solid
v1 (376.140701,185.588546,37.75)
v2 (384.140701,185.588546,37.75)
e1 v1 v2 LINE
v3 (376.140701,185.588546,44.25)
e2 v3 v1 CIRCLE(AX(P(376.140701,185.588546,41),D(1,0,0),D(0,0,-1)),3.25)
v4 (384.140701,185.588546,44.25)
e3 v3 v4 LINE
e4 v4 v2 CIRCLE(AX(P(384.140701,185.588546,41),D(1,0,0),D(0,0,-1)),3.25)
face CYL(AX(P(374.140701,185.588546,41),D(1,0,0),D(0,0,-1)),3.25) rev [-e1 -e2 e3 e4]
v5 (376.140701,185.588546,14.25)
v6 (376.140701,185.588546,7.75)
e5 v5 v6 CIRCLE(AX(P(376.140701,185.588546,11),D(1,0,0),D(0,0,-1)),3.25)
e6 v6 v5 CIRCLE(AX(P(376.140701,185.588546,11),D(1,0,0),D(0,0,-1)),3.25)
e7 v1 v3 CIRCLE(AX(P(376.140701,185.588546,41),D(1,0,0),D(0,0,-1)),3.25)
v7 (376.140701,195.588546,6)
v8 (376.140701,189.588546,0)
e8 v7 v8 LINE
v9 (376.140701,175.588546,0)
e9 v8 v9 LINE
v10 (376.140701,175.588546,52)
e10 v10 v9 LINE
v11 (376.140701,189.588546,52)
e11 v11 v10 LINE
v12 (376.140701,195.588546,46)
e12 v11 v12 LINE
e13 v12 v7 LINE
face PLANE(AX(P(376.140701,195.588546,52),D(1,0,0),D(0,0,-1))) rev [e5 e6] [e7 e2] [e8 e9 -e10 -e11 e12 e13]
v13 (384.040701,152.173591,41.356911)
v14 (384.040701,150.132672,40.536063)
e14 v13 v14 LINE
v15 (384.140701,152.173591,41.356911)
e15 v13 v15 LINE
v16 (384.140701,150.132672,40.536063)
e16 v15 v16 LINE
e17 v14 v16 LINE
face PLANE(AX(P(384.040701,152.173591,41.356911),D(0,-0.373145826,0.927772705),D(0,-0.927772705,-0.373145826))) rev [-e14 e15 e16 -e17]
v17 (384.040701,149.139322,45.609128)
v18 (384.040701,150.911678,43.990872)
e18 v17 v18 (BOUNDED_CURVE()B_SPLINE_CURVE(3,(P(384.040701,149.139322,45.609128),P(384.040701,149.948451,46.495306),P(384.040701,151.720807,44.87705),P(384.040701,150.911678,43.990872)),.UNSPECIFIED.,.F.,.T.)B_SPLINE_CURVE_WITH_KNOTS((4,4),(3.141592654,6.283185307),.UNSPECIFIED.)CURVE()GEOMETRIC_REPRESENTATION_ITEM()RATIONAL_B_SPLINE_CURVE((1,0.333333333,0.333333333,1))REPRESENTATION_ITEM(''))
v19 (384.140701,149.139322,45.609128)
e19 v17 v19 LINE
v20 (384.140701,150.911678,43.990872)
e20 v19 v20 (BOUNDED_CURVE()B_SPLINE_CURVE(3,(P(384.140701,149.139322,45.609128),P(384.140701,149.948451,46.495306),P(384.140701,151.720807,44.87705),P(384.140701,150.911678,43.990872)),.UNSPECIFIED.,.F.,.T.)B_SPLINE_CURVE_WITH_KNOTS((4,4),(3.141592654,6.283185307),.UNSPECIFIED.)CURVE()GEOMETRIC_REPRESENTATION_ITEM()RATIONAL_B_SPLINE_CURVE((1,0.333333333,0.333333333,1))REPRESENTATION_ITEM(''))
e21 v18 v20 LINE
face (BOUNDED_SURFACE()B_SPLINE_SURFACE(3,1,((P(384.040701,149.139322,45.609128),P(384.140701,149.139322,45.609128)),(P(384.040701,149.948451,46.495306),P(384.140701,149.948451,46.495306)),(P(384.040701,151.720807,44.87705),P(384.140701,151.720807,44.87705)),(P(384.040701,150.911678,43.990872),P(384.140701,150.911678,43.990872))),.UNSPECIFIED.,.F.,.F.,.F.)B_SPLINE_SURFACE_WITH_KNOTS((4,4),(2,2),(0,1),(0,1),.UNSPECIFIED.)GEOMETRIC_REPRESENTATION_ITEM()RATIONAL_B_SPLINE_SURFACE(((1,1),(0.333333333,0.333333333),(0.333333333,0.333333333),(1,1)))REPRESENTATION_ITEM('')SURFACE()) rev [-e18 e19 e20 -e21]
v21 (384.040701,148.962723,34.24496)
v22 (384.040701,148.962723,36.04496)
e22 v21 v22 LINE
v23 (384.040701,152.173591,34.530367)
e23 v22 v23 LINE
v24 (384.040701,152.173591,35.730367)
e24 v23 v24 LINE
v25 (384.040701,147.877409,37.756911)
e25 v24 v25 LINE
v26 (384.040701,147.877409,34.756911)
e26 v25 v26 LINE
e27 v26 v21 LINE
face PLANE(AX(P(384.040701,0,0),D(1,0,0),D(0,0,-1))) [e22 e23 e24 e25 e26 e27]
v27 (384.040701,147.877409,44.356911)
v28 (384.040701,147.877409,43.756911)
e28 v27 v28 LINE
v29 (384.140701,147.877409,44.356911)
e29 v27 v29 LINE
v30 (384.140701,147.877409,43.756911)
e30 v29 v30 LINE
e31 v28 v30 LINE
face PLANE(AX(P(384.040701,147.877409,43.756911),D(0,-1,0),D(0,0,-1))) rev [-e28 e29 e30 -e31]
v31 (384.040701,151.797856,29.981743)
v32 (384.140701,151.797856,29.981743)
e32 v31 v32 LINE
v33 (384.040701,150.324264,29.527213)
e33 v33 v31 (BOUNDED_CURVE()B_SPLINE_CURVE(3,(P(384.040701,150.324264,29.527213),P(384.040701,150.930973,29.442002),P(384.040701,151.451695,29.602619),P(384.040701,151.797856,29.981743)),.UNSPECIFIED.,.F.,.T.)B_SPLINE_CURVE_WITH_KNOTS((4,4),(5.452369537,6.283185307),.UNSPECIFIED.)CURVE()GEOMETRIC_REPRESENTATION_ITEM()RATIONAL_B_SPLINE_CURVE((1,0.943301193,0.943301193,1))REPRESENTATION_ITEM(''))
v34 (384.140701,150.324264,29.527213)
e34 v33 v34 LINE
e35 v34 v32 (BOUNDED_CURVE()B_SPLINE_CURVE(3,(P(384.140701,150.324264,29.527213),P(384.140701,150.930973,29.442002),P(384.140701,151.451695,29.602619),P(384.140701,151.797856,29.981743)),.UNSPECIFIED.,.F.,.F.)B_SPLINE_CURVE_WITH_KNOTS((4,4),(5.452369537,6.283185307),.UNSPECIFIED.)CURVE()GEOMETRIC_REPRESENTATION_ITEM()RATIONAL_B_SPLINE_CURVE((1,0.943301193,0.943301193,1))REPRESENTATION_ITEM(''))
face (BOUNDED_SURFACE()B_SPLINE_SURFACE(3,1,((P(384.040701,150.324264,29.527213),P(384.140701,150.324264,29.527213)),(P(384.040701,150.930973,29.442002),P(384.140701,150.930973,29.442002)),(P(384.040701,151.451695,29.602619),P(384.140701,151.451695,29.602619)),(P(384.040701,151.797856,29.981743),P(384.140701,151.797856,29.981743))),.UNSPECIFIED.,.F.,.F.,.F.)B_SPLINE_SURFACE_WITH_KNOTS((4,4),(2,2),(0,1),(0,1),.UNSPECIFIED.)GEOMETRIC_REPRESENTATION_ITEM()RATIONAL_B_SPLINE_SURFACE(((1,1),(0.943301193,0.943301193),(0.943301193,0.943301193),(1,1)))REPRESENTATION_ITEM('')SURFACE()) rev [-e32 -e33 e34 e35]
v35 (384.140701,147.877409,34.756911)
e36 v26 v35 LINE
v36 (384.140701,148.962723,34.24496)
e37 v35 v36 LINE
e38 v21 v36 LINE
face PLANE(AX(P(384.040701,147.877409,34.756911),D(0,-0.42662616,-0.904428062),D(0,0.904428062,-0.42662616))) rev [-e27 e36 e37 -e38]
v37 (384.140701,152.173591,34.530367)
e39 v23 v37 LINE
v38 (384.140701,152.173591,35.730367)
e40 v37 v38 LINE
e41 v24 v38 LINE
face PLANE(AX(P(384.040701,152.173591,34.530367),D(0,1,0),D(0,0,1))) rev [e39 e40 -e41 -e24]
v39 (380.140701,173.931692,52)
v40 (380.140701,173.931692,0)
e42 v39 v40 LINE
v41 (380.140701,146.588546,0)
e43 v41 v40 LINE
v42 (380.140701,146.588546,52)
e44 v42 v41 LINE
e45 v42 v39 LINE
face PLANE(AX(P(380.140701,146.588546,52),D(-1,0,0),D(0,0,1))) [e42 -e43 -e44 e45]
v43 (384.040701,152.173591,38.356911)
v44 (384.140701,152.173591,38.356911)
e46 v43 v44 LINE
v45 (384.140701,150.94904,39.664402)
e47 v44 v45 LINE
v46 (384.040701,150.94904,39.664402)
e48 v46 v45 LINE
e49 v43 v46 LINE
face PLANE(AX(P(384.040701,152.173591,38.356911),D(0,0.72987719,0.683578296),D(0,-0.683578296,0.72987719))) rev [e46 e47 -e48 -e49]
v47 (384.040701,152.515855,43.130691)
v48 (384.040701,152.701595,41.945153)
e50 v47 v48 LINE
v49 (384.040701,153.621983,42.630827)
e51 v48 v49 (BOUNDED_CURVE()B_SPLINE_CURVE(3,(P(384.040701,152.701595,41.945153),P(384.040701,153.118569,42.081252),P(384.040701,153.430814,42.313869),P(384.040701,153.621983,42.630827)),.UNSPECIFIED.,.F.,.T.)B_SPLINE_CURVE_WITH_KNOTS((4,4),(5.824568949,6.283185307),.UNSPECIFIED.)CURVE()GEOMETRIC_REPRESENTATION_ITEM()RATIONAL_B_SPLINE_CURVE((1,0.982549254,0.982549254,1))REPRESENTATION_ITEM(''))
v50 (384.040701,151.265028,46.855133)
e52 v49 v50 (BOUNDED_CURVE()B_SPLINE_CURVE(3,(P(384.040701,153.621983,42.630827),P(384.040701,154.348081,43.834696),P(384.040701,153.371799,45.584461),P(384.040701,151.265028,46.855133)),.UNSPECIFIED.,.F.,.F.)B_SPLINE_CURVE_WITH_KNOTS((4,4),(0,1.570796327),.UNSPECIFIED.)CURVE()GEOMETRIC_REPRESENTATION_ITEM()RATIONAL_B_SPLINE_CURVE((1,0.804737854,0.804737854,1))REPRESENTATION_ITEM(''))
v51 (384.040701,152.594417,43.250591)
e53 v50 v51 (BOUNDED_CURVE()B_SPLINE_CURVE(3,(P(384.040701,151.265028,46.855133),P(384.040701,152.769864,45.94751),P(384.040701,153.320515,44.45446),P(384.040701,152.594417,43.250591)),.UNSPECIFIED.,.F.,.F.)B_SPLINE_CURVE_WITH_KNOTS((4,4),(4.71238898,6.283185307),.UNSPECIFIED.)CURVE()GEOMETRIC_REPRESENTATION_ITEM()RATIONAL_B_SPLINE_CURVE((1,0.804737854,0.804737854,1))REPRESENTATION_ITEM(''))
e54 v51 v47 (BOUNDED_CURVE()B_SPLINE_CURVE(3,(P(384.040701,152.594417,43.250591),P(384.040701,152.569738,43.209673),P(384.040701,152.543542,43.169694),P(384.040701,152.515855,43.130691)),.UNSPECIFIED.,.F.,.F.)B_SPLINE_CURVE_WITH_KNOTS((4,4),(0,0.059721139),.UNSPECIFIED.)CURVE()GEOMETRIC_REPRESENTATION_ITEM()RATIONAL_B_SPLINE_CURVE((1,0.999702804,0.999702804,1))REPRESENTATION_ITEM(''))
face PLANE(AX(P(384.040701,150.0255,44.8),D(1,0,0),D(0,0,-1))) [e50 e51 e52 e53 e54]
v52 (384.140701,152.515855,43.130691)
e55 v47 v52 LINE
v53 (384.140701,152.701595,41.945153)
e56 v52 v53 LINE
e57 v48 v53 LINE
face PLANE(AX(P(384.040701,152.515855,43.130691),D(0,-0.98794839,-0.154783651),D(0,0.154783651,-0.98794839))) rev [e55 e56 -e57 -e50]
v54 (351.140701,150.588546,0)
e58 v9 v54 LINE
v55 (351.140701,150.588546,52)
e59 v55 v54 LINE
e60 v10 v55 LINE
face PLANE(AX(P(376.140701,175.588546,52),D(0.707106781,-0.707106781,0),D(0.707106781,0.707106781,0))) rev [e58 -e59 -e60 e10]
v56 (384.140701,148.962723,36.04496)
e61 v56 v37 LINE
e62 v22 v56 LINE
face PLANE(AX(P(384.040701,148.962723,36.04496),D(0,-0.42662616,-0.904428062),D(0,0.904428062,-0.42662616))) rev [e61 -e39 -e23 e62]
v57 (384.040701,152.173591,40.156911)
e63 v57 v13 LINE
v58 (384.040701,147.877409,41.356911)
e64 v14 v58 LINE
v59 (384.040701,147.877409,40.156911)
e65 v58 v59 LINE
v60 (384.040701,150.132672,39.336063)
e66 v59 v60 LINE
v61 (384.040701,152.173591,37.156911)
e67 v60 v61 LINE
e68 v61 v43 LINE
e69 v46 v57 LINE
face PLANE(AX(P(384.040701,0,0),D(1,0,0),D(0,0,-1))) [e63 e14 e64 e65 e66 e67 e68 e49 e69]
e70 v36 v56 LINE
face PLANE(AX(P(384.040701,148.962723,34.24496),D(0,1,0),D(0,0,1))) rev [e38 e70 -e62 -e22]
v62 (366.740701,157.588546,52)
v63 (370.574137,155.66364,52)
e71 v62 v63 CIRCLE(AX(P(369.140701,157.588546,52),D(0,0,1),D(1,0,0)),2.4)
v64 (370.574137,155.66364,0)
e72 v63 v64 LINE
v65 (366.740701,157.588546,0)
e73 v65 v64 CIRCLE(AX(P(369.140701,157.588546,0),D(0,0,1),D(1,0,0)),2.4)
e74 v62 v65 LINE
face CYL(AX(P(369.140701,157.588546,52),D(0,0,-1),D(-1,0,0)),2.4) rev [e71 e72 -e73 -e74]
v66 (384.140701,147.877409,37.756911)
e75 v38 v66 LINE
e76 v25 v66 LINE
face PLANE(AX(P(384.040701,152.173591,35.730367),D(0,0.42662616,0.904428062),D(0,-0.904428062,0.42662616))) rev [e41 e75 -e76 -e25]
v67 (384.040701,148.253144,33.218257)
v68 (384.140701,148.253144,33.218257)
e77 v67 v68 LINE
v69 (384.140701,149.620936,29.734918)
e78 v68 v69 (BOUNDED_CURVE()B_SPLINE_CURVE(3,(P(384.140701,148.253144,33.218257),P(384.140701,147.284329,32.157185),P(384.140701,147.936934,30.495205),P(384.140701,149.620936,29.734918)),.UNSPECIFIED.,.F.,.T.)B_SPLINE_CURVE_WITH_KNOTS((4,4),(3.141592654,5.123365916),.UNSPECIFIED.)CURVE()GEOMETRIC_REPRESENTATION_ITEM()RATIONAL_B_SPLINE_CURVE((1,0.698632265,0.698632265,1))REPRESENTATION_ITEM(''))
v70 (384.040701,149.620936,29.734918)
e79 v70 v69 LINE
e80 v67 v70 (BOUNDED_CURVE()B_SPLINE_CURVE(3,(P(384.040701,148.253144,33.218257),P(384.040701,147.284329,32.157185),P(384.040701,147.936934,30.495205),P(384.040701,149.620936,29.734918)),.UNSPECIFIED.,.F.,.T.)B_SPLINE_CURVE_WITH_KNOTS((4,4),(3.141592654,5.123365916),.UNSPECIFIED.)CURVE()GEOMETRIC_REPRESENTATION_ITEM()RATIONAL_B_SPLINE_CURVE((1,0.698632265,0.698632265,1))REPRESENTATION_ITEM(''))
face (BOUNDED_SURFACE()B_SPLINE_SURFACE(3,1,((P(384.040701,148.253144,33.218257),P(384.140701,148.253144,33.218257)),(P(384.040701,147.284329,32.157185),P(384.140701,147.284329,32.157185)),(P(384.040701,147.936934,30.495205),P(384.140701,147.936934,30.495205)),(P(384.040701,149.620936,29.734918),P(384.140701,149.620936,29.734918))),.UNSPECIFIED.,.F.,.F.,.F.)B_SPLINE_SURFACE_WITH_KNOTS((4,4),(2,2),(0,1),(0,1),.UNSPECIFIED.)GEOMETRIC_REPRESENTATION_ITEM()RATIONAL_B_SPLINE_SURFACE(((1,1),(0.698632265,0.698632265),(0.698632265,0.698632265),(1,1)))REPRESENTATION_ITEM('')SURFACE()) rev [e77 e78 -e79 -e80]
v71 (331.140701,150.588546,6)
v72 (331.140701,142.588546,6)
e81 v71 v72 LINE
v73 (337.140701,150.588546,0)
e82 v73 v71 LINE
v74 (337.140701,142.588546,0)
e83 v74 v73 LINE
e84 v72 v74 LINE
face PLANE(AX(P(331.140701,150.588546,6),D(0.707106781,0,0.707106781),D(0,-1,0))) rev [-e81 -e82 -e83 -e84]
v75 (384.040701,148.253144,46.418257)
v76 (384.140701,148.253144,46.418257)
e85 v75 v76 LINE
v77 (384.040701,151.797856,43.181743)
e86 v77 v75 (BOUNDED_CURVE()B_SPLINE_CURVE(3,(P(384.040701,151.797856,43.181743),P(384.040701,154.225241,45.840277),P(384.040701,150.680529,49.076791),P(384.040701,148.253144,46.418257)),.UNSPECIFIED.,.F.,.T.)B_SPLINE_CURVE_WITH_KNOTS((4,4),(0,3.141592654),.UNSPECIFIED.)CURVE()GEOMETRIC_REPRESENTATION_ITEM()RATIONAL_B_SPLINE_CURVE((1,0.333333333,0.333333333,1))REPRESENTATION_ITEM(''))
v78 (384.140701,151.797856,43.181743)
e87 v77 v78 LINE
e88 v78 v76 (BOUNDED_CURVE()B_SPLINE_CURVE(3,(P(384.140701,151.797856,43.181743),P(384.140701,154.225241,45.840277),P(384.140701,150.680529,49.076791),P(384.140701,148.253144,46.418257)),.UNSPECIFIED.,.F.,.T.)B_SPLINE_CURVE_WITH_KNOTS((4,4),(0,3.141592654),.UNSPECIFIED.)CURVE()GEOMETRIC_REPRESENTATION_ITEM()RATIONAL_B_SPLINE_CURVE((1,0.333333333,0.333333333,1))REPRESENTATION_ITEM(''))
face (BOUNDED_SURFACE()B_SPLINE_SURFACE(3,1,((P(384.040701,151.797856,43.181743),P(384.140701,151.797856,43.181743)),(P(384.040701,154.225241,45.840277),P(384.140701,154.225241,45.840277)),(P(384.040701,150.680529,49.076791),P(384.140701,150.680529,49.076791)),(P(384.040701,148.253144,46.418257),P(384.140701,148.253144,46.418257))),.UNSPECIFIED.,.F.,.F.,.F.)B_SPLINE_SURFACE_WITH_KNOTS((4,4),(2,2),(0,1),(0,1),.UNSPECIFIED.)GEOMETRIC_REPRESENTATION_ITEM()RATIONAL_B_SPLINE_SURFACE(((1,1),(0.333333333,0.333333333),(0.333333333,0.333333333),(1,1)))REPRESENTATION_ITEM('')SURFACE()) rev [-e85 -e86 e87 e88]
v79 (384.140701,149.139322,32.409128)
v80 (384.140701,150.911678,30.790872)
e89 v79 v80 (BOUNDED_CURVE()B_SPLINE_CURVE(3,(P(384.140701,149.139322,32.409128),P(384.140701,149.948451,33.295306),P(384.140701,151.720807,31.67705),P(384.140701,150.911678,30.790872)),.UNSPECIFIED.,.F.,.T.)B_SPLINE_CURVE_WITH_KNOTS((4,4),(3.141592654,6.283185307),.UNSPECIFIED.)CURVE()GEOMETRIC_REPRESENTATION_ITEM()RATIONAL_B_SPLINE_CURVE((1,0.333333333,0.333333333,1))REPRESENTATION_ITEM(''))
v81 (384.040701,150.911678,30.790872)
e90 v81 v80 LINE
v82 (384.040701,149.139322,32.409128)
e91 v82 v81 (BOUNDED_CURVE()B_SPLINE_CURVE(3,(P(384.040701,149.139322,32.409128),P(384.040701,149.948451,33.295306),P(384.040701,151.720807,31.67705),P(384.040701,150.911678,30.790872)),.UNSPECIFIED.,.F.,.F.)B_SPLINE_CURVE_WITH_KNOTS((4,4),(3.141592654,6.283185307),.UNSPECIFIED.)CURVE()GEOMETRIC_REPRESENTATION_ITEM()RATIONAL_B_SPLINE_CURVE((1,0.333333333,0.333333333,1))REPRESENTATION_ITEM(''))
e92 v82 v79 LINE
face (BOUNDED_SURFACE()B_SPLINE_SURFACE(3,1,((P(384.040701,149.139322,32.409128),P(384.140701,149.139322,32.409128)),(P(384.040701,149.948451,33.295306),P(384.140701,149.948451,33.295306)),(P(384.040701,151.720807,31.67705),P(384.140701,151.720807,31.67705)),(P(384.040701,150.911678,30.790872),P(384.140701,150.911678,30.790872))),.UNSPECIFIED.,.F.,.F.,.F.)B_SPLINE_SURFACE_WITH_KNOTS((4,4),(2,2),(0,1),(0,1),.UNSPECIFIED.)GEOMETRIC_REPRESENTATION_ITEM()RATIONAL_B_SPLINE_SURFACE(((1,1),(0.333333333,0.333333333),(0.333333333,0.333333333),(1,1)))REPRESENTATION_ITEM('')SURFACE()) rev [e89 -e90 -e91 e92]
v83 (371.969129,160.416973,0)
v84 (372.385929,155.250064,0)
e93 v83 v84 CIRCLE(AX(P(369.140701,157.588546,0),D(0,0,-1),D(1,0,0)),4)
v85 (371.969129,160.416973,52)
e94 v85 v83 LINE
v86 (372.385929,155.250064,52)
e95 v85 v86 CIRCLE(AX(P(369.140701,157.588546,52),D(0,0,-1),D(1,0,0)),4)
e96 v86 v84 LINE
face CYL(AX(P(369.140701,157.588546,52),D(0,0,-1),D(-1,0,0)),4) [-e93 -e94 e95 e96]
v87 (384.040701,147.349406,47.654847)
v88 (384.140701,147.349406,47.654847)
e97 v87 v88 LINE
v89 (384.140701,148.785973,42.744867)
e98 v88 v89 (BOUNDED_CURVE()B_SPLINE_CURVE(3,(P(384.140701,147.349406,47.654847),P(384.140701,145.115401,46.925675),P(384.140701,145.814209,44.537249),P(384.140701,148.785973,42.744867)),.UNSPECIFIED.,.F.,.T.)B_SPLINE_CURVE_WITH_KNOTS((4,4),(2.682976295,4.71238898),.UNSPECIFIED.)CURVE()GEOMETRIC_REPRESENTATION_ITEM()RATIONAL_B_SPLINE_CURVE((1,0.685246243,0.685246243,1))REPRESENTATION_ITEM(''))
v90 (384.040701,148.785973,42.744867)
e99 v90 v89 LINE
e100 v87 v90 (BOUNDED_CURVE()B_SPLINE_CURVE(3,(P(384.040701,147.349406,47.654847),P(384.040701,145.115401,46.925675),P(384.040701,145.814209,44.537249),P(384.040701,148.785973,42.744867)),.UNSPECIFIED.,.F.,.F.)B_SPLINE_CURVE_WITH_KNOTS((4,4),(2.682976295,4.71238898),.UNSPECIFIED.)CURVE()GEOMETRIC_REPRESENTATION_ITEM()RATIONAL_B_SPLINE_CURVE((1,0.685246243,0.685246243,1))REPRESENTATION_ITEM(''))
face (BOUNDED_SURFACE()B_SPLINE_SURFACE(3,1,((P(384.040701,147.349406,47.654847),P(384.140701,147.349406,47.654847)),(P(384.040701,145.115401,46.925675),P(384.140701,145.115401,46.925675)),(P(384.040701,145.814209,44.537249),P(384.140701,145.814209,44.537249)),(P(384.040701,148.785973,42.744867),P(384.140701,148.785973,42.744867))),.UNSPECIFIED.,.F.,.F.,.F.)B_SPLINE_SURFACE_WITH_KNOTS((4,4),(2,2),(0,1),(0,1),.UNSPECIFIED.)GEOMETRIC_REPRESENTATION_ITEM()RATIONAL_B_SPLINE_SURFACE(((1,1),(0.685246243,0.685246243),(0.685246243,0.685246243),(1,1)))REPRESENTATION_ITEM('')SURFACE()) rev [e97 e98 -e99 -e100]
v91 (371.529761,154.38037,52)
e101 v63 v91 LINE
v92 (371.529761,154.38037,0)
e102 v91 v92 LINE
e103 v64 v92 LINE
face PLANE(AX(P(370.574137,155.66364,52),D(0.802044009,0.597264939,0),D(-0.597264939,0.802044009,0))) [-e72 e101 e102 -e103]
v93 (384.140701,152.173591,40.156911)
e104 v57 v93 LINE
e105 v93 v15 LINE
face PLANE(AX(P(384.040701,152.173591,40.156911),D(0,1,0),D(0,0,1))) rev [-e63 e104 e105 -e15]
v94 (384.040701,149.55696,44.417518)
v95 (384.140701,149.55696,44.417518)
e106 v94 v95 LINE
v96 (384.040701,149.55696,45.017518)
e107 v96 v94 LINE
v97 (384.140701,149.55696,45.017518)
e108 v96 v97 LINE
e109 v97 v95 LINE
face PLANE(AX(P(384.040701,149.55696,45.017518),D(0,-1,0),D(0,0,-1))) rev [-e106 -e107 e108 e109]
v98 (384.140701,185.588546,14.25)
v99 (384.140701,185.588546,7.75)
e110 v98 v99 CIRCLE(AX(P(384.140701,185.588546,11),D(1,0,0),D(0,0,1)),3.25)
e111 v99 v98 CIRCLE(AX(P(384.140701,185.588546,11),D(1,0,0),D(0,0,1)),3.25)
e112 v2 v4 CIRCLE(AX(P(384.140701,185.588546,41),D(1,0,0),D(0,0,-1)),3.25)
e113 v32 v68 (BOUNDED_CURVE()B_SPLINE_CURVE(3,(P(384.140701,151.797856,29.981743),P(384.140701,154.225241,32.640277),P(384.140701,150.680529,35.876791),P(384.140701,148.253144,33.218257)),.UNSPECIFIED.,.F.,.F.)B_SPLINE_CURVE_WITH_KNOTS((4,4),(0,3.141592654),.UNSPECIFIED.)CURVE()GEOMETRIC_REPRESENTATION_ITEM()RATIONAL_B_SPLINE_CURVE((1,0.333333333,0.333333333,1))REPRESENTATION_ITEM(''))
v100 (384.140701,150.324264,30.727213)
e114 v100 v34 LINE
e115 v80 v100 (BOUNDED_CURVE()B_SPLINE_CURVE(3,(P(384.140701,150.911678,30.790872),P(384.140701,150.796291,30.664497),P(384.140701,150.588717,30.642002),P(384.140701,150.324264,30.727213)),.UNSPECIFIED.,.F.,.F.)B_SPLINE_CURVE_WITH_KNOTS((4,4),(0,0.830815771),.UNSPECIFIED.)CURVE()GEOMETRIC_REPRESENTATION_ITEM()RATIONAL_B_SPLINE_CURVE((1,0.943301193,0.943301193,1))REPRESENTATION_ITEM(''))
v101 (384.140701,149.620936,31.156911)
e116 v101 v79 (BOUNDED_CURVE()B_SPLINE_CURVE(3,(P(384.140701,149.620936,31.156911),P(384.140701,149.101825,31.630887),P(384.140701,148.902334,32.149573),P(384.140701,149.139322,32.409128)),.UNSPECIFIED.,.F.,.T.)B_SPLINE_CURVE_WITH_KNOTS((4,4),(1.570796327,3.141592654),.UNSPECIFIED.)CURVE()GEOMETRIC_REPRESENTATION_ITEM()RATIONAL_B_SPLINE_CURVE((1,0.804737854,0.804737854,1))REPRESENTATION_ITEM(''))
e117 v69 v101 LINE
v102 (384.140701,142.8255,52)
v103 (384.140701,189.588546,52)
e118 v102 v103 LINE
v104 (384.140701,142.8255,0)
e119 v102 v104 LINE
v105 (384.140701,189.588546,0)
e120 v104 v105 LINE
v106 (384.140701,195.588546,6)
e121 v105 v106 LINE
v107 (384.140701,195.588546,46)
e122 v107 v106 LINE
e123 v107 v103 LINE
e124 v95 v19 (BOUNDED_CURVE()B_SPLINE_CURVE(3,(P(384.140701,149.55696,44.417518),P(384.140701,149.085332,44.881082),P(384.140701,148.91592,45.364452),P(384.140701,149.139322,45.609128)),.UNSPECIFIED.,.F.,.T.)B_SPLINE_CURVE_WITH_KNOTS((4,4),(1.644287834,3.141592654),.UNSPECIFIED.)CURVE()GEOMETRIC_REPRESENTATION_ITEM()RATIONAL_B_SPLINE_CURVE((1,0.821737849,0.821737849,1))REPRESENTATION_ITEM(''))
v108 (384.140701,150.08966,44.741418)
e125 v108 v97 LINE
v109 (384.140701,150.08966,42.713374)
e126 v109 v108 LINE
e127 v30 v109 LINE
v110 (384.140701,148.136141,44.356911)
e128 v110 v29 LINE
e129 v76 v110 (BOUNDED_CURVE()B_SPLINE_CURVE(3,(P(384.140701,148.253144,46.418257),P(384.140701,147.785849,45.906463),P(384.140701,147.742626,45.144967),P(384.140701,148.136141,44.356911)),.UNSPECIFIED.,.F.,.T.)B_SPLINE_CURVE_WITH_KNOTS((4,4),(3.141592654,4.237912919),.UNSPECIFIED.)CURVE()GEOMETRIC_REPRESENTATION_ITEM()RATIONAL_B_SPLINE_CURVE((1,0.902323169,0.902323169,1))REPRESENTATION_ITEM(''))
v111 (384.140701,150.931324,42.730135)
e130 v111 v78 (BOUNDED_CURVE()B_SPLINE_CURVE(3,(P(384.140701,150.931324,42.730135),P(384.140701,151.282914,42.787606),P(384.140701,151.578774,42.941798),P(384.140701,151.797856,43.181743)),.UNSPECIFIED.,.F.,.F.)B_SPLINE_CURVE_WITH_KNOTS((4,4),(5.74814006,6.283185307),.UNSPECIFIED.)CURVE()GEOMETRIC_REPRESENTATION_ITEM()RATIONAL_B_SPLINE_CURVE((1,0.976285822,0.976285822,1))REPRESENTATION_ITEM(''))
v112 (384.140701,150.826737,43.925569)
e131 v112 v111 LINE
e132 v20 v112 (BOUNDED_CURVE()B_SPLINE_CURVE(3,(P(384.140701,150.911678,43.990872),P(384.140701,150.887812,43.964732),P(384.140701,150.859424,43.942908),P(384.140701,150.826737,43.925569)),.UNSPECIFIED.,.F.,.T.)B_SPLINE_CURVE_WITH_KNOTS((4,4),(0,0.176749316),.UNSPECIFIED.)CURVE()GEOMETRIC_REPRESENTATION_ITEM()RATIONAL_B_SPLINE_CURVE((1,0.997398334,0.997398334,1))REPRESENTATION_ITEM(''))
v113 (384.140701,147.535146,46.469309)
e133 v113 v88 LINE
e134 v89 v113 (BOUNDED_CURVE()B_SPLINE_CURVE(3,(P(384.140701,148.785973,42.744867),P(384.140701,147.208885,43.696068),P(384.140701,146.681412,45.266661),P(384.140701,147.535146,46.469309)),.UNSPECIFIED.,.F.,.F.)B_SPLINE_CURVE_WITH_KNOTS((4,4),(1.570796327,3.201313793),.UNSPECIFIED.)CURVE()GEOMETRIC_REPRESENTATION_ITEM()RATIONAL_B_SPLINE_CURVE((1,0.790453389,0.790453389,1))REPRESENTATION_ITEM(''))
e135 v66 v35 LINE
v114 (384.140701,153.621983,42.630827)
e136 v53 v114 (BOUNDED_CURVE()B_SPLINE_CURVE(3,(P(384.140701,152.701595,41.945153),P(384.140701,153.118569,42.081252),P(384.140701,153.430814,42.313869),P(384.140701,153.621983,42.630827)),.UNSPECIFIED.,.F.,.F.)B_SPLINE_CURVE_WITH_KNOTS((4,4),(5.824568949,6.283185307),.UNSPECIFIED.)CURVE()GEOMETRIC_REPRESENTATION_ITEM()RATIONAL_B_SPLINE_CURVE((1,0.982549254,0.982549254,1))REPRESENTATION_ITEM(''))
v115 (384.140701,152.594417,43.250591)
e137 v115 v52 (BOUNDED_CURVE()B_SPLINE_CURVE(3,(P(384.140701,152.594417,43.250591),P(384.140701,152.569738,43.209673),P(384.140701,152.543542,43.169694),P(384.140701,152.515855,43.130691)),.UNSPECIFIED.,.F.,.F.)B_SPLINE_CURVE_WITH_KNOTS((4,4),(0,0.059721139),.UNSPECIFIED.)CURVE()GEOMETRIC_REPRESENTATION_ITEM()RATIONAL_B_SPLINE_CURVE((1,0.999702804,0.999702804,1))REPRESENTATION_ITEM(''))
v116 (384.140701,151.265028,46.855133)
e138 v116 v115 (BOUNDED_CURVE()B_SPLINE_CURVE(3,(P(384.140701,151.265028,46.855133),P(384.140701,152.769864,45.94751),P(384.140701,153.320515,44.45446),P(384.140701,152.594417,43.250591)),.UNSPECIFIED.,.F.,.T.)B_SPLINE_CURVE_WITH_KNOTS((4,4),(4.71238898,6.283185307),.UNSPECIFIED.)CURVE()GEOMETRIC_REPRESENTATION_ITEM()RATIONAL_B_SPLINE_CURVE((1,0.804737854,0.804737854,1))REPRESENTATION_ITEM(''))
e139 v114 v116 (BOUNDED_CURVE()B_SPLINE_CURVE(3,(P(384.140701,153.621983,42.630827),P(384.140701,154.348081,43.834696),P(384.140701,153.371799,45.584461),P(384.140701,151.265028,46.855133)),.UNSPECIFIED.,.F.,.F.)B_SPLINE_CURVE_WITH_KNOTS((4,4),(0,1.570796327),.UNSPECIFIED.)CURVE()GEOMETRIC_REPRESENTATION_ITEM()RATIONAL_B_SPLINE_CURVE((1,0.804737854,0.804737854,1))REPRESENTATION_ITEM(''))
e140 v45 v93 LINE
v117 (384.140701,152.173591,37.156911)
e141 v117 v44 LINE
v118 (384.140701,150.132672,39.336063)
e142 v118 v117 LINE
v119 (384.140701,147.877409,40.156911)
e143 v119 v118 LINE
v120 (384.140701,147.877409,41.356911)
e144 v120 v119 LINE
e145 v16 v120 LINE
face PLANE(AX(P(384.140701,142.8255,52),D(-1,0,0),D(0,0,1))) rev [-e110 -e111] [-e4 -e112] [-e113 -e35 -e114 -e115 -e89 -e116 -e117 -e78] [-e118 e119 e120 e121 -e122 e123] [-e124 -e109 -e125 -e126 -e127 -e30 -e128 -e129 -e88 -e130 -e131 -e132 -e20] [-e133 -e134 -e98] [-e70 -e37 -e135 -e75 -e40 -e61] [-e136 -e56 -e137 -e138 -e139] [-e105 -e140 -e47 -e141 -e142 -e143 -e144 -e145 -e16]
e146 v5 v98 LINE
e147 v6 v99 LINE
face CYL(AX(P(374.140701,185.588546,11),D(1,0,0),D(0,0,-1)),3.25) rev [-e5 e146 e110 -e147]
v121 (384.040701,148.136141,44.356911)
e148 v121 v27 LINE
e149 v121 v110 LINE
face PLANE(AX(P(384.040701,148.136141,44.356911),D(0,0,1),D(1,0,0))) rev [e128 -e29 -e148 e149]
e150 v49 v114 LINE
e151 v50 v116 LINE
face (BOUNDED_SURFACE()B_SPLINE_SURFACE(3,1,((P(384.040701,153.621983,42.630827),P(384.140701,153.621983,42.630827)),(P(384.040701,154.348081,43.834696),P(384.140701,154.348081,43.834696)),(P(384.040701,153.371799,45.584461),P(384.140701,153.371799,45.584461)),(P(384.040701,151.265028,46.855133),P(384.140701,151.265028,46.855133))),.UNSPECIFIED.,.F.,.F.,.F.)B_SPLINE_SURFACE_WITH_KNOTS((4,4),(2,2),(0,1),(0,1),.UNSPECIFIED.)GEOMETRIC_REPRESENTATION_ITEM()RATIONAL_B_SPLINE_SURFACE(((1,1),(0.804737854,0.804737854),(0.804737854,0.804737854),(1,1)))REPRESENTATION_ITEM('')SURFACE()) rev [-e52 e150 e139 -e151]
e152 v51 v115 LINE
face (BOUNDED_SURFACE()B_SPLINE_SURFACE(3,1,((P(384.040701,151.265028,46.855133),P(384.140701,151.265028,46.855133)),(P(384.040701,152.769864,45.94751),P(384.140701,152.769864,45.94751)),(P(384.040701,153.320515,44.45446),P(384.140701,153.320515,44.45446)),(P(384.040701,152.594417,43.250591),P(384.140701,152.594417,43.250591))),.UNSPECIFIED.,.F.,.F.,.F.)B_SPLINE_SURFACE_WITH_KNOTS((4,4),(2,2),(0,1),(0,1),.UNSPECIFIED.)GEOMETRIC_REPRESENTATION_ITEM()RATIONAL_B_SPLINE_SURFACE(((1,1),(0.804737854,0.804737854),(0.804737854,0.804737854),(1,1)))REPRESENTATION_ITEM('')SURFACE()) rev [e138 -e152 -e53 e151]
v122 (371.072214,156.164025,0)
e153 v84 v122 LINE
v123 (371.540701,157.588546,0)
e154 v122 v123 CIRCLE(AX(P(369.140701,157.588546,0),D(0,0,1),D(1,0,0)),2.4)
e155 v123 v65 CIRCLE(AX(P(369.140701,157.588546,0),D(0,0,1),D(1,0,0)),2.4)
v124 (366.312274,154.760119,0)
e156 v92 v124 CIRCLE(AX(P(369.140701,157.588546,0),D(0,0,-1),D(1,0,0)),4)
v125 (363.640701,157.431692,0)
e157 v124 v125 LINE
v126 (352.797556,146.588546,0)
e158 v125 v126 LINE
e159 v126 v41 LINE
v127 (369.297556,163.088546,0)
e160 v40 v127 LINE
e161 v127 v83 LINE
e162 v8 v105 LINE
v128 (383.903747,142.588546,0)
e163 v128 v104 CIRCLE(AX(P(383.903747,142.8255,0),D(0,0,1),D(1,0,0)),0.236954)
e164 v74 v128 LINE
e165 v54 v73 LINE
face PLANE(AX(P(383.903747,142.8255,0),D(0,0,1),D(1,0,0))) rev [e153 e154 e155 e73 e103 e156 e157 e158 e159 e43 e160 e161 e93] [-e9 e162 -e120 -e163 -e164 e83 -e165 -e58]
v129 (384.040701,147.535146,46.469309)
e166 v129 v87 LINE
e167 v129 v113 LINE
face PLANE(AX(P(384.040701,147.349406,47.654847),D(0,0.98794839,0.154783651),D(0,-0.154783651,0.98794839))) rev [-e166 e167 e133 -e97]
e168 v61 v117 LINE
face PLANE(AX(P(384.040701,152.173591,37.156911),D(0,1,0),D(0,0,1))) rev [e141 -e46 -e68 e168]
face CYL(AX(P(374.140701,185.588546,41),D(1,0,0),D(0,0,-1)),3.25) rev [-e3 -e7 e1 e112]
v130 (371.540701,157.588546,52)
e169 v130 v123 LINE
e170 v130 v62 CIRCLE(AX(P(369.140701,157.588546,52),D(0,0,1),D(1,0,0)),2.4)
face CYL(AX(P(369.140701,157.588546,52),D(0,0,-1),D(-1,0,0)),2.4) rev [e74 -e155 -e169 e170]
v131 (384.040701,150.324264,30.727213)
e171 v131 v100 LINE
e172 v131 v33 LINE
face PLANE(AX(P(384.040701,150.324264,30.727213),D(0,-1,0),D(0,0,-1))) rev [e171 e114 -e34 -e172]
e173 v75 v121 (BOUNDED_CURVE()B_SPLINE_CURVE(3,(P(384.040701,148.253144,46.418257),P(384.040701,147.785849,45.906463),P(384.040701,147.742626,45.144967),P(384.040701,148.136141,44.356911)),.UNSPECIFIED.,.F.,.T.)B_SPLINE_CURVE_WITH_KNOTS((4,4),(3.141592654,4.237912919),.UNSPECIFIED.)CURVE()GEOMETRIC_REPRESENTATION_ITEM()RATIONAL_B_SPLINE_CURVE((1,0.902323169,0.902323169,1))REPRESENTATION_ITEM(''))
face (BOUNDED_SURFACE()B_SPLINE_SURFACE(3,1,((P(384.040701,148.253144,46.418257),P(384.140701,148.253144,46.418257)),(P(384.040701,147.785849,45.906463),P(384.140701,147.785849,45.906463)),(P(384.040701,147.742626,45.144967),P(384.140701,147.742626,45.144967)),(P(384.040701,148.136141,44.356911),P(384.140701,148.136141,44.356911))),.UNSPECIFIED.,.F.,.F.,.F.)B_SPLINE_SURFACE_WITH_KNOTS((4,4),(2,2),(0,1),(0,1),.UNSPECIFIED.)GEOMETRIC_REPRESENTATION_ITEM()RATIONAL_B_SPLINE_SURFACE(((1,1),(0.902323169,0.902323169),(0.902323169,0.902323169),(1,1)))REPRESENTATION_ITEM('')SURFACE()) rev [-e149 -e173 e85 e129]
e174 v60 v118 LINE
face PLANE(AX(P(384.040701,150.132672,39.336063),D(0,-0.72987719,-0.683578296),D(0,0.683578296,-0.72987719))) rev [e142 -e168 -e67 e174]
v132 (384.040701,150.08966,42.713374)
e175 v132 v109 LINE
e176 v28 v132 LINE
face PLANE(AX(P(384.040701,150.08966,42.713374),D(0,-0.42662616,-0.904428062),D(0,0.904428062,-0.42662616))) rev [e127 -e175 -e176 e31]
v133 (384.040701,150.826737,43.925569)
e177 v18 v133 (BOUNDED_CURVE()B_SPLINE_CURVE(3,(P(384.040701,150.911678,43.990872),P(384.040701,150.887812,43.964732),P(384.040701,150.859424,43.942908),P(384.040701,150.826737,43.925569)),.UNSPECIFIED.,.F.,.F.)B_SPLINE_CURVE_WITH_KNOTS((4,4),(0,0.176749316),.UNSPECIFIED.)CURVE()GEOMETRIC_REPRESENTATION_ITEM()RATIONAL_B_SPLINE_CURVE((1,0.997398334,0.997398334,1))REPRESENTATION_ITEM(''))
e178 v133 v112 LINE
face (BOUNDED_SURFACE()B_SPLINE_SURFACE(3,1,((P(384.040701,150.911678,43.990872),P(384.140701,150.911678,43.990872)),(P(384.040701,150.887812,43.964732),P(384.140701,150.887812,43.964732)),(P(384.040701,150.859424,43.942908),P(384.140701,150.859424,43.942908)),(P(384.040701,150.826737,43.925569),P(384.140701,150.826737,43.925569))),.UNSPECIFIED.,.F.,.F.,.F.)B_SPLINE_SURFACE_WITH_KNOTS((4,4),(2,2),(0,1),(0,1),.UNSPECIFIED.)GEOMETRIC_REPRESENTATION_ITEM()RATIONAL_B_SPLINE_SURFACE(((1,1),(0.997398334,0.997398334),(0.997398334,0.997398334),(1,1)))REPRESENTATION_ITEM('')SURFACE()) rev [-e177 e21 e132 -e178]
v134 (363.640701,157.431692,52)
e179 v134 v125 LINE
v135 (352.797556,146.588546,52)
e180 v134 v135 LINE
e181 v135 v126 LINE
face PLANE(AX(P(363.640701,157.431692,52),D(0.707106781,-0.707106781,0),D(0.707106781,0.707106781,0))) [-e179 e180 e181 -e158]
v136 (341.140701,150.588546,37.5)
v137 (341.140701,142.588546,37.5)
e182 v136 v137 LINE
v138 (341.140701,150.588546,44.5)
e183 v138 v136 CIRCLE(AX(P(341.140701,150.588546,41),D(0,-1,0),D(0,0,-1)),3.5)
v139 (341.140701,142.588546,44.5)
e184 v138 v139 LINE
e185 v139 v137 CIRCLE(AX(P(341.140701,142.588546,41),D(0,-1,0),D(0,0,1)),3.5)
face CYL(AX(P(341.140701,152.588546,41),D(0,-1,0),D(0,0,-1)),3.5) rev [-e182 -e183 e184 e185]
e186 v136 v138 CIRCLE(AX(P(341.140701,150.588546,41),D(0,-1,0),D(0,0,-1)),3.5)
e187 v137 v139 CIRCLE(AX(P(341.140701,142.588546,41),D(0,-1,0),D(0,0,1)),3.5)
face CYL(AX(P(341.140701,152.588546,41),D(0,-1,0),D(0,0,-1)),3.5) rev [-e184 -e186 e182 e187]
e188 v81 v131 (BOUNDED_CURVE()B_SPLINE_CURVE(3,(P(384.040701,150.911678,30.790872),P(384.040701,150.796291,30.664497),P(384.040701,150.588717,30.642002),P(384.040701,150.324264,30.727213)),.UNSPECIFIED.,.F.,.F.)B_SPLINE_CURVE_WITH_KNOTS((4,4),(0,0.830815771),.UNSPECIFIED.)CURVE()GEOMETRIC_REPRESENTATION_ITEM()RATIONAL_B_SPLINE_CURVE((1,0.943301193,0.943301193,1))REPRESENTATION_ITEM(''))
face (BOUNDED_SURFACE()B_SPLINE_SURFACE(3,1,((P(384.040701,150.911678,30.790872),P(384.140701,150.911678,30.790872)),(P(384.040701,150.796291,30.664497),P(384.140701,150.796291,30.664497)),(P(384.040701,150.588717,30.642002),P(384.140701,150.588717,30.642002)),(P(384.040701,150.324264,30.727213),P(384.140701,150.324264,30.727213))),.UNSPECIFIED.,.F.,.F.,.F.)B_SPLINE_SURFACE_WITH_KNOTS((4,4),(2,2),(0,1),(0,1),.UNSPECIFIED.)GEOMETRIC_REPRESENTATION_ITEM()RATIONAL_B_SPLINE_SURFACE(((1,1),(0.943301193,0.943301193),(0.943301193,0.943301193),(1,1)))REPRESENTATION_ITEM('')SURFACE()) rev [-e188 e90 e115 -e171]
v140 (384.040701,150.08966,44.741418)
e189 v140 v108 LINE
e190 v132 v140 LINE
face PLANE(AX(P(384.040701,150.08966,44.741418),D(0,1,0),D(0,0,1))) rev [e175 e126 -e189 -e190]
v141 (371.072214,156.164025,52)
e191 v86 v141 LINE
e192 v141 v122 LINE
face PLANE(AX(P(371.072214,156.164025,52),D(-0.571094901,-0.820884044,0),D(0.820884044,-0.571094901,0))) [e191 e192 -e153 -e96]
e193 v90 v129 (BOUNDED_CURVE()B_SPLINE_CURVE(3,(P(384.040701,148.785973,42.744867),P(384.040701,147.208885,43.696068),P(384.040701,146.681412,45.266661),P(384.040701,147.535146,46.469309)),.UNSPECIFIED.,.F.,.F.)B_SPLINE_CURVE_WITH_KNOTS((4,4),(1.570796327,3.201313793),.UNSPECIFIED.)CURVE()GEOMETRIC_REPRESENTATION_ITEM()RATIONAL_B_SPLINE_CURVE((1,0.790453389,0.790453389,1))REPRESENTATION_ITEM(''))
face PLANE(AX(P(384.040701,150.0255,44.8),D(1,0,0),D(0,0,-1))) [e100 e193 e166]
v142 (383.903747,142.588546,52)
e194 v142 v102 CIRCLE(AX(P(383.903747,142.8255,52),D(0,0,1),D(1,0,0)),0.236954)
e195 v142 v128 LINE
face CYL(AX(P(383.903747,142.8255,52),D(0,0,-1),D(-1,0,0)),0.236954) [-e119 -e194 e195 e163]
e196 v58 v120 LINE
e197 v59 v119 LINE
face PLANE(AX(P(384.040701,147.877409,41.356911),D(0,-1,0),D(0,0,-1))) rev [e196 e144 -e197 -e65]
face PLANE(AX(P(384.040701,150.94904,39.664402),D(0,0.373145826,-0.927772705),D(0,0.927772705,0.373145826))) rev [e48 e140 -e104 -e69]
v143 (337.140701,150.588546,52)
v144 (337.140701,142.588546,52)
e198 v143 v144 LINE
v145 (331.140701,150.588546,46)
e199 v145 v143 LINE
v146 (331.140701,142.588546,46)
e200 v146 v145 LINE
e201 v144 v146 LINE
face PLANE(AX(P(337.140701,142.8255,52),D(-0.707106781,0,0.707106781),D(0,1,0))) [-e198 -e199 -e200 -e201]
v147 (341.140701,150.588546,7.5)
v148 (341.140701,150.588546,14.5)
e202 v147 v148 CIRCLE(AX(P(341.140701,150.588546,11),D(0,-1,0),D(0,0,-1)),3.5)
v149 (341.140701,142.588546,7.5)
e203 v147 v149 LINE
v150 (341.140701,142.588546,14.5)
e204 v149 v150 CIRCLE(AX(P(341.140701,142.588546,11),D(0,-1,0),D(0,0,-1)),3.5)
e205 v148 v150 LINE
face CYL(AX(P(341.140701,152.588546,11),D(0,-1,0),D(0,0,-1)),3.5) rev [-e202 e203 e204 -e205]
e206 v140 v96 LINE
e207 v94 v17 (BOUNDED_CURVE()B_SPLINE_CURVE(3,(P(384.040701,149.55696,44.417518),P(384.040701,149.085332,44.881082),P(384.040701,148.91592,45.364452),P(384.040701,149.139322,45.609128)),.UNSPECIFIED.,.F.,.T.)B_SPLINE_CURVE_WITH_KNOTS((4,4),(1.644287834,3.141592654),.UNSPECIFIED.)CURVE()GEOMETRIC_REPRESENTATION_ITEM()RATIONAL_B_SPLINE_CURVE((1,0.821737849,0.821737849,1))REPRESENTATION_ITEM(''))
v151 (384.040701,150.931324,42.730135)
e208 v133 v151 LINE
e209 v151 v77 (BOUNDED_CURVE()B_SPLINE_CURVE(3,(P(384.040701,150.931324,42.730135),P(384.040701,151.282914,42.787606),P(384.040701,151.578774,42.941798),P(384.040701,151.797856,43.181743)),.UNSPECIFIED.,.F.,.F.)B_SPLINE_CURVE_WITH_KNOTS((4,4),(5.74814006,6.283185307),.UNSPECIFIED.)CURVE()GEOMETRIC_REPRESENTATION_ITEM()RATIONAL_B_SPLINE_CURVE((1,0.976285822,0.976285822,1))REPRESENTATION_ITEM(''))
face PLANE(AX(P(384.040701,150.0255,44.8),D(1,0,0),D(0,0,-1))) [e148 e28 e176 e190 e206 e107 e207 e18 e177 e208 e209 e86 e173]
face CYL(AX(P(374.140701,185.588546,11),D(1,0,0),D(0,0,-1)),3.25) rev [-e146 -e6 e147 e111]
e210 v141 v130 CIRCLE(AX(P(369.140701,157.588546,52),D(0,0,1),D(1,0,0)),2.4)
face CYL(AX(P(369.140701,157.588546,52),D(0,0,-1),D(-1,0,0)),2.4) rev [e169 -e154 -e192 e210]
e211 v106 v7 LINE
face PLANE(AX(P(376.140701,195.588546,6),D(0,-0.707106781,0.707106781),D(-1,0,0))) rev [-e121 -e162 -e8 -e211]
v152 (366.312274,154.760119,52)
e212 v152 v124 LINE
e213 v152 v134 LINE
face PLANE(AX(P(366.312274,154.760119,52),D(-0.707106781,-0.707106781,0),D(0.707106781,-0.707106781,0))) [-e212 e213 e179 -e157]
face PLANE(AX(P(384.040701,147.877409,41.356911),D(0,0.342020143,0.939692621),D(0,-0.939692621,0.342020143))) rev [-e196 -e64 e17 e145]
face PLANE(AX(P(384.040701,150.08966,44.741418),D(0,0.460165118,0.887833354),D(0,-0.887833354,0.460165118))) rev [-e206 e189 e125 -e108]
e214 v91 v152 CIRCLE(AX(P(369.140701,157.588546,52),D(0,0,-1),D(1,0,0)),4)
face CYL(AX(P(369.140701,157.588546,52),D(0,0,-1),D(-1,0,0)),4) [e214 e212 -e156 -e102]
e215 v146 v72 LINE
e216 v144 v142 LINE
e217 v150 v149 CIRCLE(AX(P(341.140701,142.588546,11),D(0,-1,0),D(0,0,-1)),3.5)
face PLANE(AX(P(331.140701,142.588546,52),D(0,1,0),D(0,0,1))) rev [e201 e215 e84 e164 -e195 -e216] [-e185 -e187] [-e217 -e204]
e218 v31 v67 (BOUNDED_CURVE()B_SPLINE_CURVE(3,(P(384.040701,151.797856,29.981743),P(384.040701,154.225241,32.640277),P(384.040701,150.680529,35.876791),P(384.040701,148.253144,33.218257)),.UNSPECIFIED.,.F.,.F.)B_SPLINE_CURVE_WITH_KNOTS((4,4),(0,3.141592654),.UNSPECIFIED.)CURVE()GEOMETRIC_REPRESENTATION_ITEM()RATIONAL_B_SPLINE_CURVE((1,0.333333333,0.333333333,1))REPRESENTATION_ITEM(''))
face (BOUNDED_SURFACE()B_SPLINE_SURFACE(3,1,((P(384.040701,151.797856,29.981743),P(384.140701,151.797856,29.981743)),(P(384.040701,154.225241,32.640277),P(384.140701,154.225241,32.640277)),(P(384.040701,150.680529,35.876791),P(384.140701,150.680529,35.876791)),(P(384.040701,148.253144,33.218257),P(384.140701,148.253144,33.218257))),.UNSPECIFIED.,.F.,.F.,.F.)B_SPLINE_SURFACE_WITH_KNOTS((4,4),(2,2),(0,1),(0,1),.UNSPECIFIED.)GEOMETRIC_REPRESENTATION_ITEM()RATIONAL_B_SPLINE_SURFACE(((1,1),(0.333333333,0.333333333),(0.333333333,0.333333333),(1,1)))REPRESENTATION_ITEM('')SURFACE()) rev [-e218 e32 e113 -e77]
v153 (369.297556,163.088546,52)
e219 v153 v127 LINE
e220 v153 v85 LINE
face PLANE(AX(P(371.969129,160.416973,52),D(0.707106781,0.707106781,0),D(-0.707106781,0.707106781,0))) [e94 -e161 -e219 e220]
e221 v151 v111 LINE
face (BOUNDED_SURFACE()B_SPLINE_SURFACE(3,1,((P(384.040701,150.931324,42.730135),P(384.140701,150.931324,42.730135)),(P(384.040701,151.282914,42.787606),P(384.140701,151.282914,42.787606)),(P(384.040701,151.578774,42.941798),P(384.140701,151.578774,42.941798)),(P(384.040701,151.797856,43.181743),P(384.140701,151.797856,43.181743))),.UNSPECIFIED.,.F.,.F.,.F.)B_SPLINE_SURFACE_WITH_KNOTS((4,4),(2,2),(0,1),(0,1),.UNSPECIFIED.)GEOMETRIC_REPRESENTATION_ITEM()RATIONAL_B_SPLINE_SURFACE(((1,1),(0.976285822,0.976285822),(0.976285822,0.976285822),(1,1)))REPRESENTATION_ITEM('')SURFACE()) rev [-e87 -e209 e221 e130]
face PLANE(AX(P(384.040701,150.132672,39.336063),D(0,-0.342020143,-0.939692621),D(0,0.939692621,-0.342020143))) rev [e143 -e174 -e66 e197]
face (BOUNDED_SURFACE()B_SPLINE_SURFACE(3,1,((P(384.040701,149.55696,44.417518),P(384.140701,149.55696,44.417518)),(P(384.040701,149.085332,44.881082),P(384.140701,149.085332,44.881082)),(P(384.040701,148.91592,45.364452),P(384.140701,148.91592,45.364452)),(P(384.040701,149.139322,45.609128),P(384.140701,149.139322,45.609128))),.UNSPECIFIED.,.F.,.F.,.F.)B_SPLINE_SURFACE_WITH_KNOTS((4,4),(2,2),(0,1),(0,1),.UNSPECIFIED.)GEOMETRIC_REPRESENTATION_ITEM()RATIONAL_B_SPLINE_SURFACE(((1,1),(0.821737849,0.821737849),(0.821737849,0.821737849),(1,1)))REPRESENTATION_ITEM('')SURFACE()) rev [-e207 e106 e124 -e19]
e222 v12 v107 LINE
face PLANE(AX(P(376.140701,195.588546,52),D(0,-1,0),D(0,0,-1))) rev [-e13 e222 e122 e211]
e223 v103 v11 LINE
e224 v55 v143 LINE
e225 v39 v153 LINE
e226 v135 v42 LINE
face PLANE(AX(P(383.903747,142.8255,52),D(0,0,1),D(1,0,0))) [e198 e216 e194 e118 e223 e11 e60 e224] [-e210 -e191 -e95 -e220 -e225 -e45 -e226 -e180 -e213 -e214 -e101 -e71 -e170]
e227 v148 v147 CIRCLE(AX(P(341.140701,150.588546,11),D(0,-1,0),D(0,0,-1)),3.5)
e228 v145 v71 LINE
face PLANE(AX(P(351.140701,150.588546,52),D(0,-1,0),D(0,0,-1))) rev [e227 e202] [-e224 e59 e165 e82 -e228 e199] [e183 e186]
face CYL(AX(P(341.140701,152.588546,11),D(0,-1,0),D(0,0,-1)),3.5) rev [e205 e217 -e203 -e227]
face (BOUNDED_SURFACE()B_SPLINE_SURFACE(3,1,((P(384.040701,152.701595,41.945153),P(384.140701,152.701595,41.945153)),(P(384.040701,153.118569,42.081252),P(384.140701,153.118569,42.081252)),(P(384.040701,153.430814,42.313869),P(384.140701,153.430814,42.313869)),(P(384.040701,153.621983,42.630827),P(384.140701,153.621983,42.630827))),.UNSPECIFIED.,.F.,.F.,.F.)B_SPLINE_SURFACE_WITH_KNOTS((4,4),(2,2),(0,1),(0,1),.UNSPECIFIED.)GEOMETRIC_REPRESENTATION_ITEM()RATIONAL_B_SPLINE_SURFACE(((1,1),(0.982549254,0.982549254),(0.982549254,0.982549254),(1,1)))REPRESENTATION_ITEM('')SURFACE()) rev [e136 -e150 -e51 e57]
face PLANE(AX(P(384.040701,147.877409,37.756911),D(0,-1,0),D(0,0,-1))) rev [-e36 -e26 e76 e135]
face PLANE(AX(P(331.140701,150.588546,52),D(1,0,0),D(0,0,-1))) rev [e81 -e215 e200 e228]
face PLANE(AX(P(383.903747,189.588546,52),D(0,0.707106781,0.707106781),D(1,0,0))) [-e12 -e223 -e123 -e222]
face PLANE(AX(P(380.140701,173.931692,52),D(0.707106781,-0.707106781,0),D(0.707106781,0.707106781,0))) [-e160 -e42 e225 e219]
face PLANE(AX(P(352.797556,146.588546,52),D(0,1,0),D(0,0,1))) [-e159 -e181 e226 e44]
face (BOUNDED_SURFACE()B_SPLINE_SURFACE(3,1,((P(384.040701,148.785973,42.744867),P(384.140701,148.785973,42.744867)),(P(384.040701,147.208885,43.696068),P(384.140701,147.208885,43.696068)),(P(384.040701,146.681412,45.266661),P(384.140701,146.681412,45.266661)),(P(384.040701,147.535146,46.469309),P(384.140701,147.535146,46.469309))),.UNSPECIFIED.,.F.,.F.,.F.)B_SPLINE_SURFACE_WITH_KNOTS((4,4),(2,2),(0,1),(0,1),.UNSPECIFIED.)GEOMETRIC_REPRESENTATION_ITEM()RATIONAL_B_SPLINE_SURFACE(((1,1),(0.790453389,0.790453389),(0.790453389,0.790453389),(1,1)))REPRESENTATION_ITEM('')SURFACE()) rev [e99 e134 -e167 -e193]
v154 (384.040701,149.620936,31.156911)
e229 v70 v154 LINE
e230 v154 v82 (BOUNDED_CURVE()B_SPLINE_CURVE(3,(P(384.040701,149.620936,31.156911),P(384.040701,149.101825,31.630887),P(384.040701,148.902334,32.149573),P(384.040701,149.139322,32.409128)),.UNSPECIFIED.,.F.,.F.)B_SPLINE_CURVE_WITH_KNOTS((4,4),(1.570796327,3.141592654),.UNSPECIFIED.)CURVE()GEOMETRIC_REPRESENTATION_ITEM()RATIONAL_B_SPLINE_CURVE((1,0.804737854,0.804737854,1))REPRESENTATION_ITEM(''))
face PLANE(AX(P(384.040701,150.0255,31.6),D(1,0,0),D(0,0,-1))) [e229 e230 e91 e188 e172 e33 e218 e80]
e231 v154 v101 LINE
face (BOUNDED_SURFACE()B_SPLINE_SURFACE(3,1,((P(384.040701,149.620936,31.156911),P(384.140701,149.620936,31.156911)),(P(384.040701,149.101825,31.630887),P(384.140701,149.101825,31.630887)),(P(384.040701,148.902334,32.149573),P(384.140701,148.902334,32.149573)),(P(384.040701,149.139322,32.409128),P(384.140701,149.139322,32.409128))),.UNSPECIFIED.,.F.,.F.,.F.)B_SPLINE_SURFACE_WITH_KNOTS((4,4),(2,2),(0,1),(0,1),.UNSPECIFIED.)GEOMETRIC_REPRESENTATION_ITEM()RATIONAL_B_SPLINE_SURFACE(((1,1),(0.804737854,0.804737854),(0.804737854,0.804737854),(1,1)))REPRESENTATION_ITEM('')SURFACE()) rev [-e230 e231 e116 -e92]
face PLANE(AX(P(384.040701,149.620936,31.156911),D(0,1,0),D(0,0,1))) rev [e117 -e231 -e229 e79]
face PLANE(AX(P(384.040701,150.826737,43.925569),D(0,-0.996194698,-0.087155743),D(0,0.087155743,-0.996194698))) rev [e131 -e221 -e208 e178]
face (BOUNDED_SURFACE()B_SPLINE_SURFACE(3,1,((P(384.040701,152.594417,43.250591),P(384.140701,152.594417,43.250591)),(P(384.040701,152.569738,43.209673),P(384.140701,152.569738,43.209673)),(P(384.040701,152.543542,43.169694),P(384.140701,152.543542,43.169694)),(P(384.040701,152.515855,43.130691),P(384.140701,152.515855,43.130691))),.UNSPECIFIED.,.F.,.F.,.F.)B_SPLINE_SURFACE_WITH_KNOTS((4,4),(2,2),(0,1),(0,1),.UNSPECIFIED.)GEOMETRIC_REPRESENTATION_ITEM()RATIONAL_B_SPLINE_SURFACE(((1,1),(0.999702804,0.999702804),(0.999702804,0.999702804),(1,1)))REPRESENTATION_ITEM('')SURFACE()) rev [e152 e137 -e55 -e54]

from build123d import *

# Parameters (mm, degrees)
EXTRUDE_1_DEPTH     = 52
SKETCH_1_R          = 3.5
CUT_EXTRUDE_1_DEPTH = 10
SKETCH_3_R          = 3.25
CUT_EXTRUDE_2_DEPTH = 10
CUT_EXTRUDE_3_DEPTH = 0.1
CHAMFER_2_SIZE      = 6


with BuildPart() as part:
    # Model → 凸台-拉伸1 (new body)
    with BuildSketch(Plane.XY):
        with BuildLine():
            Line((376.14070145, 195.588546008), (384.14070145, 195.588546008))
            Line((384.14070145, 195.588546008), (384.14070145, 142.825500368))
            ThreePointArc((384.14070145, 142.825500368), (384.071299125, 142.657948334), (383.90374709, 142.588546008))
            Line((383.90374709, 142.588546008), (331.14070145, 142.588546008))
            Line((331.14070145, 142.588546008), (331.14070145, 150.588546008))
            Line((331.14070145, 150.588546008), (351.14070145, 150.588546008))
            Line((351.14070145, 150.588546008), (376.14070145, 175.588546008))
            Line((376.14070145, 175.588546008), (376.14070145, 195.588546008))
        make_face()
        with BuildLine():
            Line((352.797555699, 146.588546008), (380.14070145, 146.588546008))
            Line((380.14070145, 146.588546008), (380.14070145, 173.931691759))
            Line((380.14070145, 173.931691759), (369.297555699, 163.088546008))
            Line((369.297555699, 163.088546008), (371.969128574, 160.416973133))
            ThreePointArc((371.969128574, 160.416973133), (373.12775021, 157.910170293), (372.385928963, 155.25006394))
            Line((372.385928963, 155.25006394), (371.072213777, 156.164024991))
            ThreePointArc((371.072213777, 156.164024991), (367.439726654, 159.281674694), (370.574137304, 155.663640387))
            Line((370.574137304, 155.663640387), (371.529761206, 154.380369972))
            ThreePointArc((371.529761206, 154.380369972), (368.850334045, 153.599099083), (366.312274325, 154.760118884))
            Line((366.312274325, 154.760118884), (363.64070145, 157.431691759))
            Line((363.64070145, 157.431691759), (352.797555699, 146.588546008))
        make_face(mode=Mode.SUBTRACT)
    extrude(amount=EXTRUDE_1_DEPTH)

    # 草图1 → 切除-拉伸1 (cut)
    with BuildSketch(Plane(origin=(0, 142.588546008, 0), x_dir=(-1, 0, 0), z_dir=(0, -1, 0))):
        with Locations(Location((-341.14070145, -11, 0), (0, 0, 90))):
            Circle(SKETCH_1_R)
        with Locations(Location((-341.14070145, -41, 0), (0, 0, 90))):
            Circle(SKETCH_1_R)
    extrude(amount=-CUT_EXTRUDE_1_DEPTH, mode=Mode.SUBTRACT)

    # 草图3 → 切除-拉伸2 (cut)
    with BuildSketch(Plane(origin=(384.14070145, 0, 0), x_dir=(0, 0, -1), z_dir=(1, 0, 0))):
        with Locations((-41, 185.588546008)):
            Circle(SKETCH_3_R)
        with Locations((-11, 185.588546008)):
            Circle(SKETCH_3_R)
    extrude(amount=-CUT_EXTRUDE_2_DEPTH, mode=Mode.SUBTRACT)

    # 草图4 → 切除-拉伸3 (cut)
    with BuildSketch(Plane(origin=(384.14070145, 0, 0), x_dir=(0, 0, -1), z_dir=(1, 0, 0))):
        with BuildLine():
            Line((-31.156910998, 149.620936237), (-29.734918025, 149.620936237))
            add(Edge.make_bspline(
                [(-29.527213106, 150.324263564), (-29.069640514, 153.582209756), (-32.160166716, 151.852897671), (-35.250692919, 150.123585587), (-33.22217607, 148.256737296), (-31.193659222, 146.389889004), (-29.734918025, 149.620936237)],
                knots=[2.310776883, 2.310776883, 2.310776883, 4.295504112, 4.295504112, 6.280231341, 6.280231341, 8.26495857, 8.26495857, 8.26495857], degree=2, weights=[1, 0.546712287, 1, 0.546712287, 1, 0.546712287, 1]))
            Line((-29.527213106, 150.324263564), (-30.727213106, 150.324263564))
            add(Edge.make_bspline(
                [(-30.727213106, 150.324263564), (-30.331693937, 151.551759326), (-31.551251149, 150.835698352), (-32.770808361, 150.119637377), (-32.499443953, 149.28370119), (-32.228079545, 148.447765002), (-31.156910998, 149.620936237)],
                knots=[2.310776883, 2.310776883, 2.310776883, 4.1585118, 4.1585118, 6.006246717, 6.006246717, 7.853981634, 7.853981634, 7.853981634], degree=2, weights=[1, 0.602738677, 1, 0.602738677, 1, 0.602738677, 1]))
        make_face()
        with BuildLine():
            Line((-43.925569034, 150.826737427), (-42.730135397, 150.931324318))
            add(Edge.make_bspline(
                [(-42.730135397, 150.931324318), (-43.532943041, 155.84269164), (-46.525470552, 150.700825597), (-49.517998063, 145.558959554), (-44.356910998, 148.136141251)],
                knots=[2.606547406, 2.606547406, 2.606547406, 4.993026489, 4.993026489, 7.379505572, 7.379505572, 7.379505572], degree=2, weights=[1, 0.368650437, 1, 0.368650437, 1]))
            Line((-44.356910998, 148.136141251), (-44.356910998, 147.877409345))
            Line((-44.356910998, 147.877409345), (-43.756910998, 147.877409345))
            Line((-43.756910998, 147.877409345), (-42.713374, 150.089660335))
            Line((-42.713374, 150.089660335), (-44.741418493, 150.089660335))
            Line((-44.741418493, 150.089660335), (-45.017517564, 149.556960323))
            Line((-45.017517564, 149.556960323), (-44.417517564, 149.556960323))
            add(Edge.make_bspline(
                [(-43.925569034, 150.826737427), (-44.690411989, 152.268585428), (-45.646229095, 149.801508889), (-46.602046201, 147.334432349), (-44.417517564, 149.556960323)],
                knots=[2.964843337, 2.964843337, 2.964843337, 5.372666732, 5.372666732, 7.780490127, 7.780490127, 7.780490127], degree=2, weights=[1, 0.358709137, 1, 0.358709137, 1]))
        make_face()
        Polygon((-41.356910998, 147.877409345), (-40.156910998, 147.877409345), (-39.336062654, 150.132671635), (-37.156910998, 152.173591391), (-38.356910998, 152.173591391), (-39.664401992, 150.949039538), (-40.156910998, 152.173591391), (-41.356910998, 152.173591391), (-40.536062654, 150.132671635), align=None)
        Polygon((-35.73036657, 152.173591391), (-37.756910998, 147.877409345), (-34.756910998, 147.877409345), (-34.244959606, 148.96272302), (-36.044959606, 148.96272302), (-34.53036657, 152.173591391), align=None)
        with BuildLine():
            Line((-43.130690832, 152.515854721), (-41.945152764, 152.701595103))
            add(Edge.make_bspline(
                [(-41.945152764, 152.701595103), (-43.36499983, 157.051657906), (-46.85513293, 151.265027956)],
                knots=[2.682976295, 2.682976295, 2.682976295, 4.71238898, 4.71238898, 4.71238898], degree=2, weights=[1, 0.527869365, 1]))
            add(Edge.make_bspline(
                [(-43.130690832, 152.515854721), (-45.210313594, 153.992133359), (-46.85513293, 151.265027956)],
                knots=[6.223464168, 6.223464168, 6.223464168, 7.853981634, 7.853981634, 7.853981634], degree=2, weights=[1, 0.685680084, 1]))
        make_face()
        with BuildLine():
            Line((-47.654847236, 147.349405634), (-46.469309168, 147.535146015))
            add(Edge.make_bspline(
                [(-46.469309168, 147.535146015), (-44.389686406, 146.058867378), (-42.74486707, 148.78597278)],
                knots=[3.081871514, 3.081871514, 3.081871514, 4.71238898, 4.71238898, 4.71238898], degree=2, weights=[1, 0.685680084, 1]))
            add(Edge.make_bspline(
                [(-47.654847236, 147.349405634), (-46.23500017, 142.999342831), (-42.74486707, 148.78597278)],
                knots=[2.682976295, 2.682976295, 2.682976295, 4.71238898, 4.71238898, 4.71238898], degree=2, weights=[1, 0.527869365, 1]))
        make_face()
    extrude(amount=-CUT_EXTRUDE_3_DEPTH, mode=Mode.SUBTRACT)

    # 倒角2
    chamfer_2_edges = [part.edges().sort_by_distance(p)[0] for p in [
        (331.14070145, 146.588546008, 52),
        (380.14070145, 195.588546008, 52),
        (380.14070145, 195.588546008, 0),
        (331.14070145, 146.588546008, 0),
    ]]
    chamfer(chamfer_2_edges, length=CHAMFER_2_SIZE)


solid = part.part
